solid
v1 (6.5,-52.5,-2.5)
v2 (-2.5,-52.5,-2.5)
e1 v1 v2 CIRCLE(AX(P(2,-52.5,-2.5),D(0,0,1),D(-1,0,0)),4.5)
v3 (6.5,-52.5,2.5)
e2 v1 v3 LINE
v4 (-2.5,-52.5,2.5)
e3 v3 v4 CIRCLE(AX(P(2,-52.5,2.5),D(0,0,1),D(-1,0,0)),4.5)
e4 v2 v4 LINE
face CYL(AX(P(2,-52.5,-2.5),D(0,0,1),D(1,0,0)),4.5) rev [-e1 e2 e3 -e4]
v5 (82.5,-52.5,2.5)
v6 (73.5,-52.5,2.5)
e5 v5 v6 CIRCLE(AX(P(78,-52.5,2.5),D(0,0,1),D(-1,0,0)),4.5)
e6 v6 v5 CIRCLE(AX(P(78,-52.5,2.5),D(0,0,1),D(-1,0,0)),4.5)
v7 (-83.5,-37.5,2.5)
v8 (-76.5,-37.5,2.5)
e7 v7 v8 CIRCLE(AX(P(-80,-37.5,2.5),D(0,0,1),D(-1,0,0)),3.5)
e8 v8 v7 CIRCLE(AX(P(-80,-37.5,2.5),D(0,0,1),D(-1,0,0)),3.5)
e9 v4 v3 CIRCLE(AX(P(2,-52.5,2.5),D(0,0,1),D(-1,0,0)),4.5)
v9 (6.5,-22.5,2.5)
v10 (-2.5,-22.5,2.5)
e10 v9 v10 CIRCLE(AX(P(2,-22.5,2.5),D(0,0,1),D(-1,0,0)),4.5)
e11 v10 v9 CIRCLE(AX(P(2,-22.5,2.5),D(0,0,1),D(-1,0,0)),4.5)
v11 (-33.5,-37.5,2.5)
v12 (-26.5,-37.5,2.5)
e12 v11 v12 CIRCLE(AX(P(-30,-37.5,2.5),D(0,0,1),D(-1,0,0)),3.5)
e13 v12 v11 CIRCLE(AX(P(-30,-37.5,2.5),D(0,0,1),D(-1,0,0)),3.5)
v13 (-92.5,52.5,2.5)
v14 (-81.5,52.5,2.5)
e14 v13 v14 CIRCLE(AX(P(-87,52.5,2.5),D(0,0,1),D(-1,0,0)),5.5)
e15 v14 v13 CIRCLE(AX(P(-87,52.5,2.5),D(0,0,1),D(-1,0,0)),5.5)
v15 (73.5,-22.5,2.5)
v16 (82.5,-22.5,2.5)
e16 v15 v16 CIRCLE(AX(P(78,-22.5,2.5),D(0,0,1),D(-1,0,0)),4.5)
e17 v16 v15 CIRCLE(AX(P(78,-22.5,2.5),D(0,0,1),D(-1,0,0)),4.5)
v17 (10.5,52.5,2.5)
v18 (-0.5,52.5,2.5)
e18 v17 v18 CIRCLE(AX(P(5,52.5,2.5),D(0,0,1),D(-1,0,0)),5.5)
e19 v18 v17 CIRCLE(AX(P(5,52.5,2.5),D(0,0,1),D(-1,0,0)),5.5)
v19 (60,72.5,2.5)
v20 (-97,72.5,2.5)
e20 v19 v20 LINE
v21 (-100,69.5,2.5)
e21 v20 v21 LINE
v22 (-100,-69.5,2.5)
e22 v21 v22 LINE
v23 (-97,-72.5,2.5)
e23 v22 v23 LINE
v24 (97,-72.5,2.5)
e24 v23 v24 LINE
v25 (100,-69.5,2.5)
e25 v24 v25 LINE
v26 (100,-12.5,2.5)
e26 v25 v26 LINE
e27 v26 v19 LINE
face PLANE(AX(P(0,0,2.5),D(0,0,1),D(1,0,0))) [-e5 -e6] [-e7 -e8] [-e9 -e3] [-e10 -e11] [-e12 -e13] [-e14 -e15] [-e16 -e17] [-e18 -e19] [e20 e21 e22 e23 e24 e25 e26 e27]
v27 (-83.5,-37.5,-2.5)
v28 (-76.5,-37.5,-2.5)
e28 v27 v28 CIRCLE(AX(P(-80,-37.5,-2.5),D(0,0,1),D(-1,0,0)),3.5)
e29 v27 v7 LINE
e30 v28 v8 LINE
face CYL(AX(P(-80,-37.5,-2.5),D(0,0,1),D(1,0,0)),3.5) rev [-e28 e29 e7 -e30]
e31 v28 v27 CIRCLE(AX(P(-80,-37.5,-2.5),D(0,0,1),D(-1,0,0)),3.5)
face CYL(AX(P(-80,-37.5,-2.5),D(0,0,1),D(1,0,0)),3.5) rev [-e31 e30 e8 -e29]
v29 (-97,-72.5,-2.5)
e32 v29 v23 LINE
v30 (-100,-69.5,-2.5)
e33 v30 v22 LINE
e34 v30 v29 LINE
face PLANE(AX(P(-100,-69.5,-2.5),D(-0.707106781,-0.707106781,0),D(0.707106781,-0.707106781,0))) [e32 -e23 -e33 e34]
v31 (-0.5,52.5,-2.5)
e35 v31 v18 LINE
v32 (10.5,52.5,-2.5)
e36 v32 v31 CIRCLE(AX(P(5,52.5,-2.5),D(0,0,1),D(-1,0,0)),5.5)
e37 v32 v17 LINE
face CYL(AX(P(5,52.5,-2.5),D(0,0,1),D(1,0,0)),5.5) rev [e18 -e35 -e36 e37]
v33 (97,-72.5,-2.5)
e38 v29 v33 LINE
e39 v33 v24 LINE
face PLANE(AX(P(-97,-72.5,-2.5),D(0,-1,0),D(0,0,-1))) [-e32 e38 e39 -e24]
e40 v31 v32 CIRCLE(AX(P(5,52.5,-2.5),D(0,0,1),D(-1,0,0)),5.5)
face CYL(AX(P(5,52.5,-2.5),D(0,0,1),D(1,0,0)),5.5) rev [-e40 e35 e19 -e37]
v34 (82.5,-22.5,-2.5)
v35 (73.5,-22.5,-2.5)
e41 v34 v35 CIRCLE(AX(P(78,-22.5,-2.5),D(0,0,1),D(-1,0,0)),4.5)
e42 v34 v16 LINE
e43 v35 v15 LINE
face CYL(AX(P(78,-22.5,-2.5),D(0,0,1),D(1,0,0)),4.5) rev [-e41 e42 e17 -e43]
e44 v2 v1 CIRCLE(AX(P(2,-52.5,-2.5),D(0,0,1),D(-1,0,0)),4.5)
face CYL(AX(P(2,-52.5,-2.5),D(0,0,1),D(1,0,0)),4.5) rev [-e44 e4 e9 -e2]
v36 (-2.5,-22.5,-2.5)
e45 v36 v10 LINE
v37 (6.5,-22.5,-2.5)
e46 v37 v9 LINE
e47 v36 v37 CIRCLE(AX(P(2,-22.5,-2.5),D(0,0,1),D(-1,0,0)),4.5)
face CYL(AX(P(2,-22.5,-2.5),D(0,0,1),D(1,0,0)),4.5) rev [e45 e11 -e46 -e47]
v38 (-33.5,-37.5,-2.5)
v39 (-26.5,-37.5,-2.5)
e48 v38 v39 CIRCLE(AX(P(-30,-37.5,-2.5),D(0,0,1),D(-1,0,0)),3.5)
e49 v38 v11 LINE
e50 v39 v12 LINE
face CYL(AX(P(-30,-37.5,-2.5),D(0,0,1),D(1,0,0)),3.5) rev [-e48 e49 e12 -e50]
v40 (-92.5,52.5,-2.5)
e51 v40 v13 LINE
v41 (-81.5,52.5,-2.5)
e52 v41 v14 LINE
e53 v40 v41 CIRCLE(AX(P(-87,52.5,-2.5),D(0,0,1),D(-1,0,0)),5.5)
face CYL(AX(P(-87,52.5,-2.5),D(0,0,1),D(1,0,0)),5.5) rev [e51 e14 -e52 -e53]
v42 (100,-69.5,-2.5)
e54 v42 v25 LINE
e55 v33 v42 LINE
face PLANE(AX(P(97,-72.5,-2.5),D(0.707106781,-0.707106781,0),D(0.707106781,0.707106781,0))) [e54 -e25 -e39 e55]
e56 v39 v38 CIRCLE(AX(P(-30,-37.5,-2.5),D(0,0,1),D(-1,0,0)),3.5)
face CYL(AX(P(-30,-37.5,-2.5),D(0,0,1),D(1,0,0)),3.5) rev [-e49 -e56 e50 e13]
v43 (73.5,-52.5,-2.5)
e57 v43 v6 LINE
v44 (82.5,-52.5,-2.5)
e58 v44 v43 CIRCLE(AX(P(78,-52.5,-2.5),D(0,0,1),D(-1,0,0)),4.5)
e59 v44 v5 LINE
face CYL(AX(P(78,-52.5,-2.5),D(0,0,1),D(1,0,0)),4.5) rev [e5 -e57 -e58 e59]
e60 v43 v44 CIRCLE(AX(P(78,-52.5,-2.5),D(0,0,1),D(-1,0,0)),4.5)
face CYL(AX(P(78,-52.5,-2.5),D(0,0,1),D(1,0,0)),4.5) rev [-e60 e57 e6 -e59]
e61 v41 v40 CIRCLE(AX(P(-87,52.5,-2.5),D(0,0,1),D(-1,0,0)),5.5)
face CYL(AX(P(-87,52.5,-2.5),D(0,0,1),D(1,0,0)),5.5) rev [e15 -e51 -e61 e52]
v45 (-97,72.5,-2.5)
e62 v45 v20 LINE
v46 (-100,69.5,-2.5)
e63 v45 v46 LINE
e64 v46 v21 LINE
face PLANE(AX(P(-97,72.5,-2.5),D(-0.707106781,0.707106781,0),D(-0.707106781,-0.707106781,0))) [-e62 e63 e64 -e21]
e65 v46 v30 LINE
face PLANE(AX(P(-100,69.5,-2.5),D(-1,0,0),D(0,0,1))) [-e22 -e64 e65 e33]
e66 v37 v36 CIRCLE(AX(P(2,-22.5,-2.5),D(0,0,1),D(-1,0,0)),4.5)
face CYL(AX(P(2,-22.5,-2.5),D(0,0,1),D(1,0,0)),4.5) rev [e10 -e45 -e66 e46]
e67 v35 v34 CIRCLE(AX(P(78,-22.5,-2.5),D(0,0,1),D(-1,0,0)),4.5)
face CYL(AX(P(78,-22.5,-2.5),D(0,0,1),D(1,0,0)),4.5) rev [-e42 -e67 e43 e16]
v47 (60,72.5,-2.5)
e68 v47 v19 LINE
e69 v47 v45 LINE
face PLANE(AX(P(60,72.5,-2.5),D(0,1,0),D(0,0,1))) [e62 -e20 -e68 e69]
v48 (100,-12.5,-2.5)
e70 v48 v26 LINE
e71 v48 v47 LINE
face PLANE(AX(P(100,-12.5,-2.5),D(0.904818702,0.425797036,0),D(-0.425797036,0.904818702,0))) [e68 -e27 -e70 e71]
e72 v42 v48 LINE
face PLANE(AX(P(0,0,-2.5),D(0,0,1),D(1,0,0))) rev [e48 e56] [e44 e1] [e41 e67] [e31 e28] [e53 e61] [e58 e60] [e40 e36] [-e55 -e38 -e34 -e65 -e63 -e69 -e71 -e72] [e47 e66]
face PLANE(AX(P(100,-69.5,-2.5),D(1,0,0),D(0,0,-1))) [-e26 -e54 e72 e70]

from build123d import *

# Parameters (mm, degrees)
SKETCH_1_R      = 4.5
SKETCH_1_R_2    = 3.5
SKETCH_1_R_3    = 5.5
EXTRUDE_1_DEPTH = 5


with BuildPart() as part:
    # 草图1 → 凸台-拉伸1 (new body)
    with BuildSketch(Plane.XY.offset(2.5)):
        Polygon((-97, -72.5), (97, -72.5), (100, -69.5), (100, -12.5), (60, 72.5), (-97, 72.5), (-100, 69.5), (-100, -69.5), align=None)
        with Locations(Location((2, -22.5, 0), (0, 0, 180))):
            Circle(SKETCH_1_R, mode=Mode.SUBTRACT)
        with Locations(Location((-30, -37.5, 0), (0, 0, 180))):
            Circle(SKETCH_1_R_2, mode=Mode.SUBTRACT)
        with Locations(Location((-80, -37.5, 0), (0, 0, 180))):
            Circle(SKETCH_1_R_2, mode=Mode.SUBTRACT)
        with Locations(Location((5, 52.5, 0), (0, 0, 180))):
            Circle(SKETCH_1_R_3, mode=Mode.SUBTRACT)
        with Locations(Location((78, -52.5, 0), (0, 0, 180))):
            Circle(SKETCH_1_R, mode=Mode.SUBTRACT)
        with Locations(Location((2, -52.5, 0), (0, 0, 180))):
            Circle(SKETCH_1_R, mode=Mode.SUBTRACT)
        with Locations(Location((78, -22.5, 0), (0, 0, 180))):
            Circle(SKETCH_1_R, mode=Mode.SUBTRACT)
        with Locations(Location((-87, 52.5, 0), (0, 0, 180))):
            Circle(SKETCH_1_R_3, mode=Mode.SUBTRACT)
    extrude(amount=-EXTRUDE_1_DEPTH)


solid = part.part
